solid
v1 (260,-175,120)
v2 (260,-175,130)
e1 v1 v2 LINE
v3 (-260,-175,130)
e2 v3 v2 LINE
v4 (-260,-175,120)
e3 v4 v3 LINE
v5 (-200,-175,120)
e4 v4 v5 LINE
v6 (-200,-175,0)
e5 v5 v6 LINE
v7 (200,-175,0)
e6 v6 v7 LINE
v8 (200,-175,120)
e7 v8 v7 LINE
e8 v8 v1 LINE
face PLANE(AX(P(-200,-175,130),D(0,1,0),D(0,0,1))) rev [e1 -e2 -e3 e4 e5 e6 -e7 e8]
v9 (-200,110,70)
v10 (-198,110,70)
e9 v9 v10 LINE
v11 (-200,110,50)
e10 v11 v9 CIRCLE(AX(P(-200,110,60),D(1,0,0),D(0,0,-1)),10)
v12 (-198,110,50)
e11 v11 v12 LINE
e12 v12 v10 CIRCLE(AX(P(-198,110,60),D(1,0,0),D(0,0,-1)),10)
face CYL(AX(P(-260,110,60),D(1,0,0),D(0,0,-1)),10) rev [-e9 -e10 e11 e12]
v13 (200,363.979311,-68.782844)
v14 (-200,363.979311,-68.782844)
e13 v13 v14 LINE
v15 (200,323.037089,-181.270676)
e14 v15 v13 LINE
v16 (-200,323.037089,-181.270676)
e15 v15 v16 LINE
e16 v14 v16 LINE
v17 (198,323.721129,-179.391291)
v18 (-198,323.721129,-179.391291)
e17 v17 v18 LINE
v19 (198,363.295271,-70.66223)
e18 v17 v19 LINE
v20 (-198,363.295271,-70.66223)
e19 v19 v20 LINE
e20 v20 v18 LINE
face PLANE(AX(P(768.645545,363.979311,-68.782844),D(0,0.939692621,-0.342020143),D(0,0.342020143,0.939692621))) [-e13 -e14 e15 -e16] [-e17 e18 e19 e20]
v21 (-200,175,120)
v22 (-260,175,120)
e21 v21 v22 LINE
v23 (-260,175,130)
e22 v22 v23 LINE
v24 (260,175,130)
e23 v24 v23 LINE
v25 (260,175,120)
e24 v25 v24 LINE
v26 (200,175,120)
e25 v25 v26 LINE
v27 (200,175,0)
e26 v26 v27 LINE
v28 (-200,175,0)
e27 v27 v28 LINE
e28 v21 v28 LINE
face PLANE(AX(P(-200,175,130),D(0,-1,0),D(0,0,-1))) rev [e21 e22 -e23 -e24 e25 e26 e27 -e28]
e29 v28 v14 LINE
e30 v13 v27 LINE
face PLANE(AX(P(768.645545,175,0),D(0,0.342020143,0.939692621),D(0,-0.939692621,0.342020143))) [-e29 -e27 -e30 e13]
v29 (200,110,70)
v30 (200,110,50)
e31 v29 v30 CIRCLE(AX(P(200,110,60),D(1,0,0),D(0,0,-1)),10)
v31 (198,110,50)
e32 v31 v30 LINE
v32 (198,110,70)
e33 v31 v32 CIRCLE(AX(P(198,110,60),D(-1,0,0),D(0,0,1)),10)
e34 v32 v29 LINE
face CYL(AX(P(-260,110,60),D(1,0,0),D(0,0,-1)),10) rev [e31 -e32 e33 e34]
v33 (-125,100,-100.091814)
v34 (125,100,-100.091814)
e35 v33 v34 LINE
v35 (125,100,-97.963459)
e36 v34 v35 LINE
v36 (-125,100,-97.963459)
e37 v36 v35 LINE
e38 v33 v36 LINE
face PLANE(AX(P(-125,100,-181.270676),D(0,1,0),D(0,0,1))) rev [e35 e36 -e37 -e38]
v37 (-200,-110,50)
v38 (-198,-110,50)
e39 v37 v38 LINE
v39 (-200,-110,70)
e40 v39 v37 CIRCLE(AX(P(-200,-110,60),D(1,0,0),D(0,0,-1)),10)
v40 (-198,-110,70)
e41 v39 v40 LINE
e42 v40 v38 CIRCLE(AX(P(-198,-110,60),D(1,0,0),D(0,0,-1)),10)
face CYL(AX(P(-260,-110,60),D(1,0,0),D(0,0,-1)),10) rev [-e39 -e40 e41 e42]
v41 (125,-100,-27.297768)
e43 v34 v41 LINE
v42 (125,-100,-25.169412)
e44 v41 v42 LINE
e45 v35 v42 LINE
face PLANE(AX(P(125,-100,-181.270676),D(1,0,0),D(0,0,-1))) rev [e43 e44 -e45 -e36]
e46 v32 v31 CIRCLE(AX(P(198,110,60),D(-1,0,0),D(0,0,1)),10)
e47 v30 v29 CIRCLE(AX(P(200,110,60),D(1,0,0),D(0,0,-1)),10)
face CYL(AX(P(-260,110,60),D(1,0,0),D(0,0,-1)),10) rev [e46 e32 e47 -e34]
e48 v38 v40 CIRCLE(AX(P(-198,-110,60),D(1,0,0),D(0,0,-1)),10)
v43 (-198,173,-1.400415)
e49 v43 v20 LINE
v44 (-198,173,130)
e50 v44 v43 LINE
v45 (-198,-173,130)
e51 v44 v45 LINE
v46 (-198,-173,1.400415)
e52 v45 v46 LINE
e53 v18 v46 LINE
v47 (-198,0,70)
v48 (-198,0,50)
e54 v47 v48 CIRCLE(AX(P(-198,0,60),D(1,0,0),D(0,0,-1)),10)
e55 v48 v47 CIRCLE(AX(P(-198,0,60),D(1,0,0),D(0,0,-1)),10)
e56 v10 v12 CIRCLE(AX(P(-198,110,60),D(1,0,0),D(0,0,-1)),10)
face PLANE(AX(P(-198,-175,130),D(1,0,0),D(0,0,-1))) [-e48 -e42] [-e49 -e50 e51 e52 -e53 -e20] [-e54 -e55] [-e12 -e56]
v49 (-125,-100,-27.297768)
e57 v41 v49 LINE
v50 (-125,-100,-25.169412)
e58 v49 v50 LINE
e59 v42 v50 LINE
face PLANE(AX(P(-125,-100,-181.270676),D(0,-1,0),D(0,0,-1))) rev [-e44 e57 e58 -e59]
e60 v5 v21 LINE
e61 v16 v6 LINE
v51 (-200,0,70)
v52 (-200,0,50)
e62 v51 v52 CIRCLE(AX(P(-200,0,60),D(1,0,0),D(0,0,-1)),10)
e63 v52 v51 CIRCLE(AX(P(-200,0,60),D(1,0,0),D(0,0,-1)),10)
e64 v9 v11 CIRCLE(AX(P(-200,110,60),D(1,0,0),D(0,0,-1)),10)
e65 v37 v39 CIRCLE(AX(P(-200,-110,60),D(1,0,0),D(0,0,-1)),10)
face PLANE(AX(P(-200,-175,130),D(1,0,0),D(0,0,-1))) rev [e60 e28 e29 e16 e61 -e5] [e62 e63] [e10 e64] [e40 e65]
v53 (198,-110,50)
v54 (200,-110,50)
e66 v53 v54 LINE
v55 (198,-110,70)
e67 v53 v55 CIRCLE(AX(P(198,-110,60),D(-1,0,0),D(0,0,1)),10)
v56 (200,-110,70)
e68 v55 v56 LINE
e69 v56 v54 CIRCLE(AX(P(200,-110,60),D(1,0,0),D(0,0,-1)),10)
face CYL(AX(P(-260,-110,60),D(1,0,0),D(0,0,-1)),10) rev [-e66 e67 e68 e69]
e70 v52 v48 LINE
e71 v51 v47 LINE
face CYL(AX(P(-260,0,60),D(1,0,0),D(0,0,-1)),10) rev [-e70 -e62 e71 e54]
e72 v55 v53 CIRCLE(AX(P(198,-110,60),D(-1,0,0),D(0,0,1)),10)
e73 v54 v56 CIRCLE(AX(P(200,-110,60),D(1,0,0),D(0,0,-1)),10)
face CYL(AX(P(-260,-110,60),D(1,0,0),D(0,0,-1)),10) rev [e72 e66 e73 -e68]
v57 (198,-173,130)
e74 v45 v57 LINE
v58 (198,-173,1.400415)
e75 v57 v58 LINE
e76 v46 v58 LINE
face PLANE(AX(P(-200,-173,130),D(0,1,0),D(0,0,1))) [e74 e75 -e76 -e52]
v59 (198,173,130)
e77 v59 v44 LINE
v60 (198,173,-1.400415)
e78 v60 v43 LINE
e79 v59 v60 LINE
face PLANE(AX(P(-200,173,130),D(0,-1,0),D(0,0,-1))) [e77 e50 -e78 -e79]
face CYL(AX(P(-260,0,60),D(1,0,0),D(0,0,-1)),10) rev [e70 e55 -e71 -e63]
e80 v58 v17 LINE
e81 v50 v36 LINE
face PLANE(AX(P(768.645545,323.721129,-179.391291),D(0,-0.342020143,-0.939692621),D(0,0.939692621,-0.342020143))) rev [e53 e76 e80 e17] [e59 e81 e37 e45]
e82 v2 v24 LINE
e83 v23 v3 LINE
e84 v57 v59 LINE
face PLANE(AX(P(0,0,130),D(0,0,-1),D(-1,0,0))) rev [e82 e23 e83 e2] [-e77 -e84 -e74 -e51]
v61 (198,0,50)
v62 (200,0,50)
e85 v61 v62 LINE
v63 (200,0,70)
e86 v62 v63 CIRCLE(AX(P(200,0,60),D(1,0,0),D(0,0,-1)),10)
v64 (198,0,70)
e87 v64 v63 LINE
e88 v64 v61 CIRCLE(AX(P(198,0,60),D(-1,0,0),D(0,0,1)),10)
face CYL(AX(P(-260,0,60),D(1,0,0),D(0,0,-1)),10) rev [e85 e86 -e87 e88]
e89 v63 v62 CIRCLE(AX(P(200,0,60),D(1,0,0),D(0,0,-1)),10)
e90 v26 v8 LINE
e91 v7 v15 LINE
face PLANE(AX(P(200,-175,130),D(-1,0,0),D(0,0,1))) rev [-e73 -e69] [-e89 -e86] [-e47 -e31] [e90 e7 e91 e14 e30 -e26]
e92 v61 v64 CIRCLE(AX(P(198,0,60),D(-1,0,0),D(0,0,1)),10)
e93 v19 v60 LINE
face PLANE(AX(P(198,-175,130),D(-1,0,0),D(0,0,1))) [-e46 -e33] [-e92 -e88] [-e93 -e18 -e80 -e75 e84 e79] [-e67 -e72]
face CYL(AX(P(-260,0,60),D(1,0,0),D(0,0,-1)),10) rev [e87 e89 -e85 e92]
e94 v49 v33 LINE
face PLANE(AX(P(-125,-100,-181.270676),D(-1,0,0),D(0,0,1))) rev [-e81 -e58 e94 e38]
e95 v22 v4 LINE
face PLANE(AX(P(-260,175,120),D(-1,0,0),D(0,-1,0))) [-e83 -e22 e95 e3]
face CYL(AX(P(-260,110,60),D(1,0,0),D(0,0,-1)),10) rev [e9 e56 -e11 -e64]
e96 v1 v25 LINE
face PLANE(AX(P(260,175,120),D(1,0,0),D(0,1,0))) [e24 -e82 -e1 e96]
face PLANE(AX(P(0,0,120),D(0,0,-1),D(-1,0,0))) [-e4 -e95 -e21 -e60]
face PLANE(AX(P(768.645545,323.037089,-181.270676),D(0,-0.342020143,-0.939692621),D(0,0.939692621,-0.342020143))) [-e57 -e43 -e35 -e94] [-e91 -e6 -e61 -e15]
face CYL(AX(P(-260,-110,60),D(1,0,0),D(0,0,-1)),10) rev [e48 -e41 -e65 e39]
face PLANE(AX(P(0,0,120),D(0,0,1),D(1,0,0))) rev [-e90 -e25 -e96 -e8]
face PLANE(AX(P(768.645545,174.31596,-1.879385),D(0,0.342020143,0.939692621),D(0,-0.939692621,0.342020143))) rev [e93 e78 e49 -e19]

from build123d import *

# Parameters (mm, degrees)
SKETCH_1_W          = 400
SKETCH_1_H          = 350
EXTRUDE_1_DEPTH     = 130
EXTRUDE_5_DEPTH     = 400
SHELL_2_T           = -2
SKETCH_3_W          = 60
SKETCH_3_H          = 350
EXTRUDE_2_DEPTH     = 10
SKETCH_8_W          = 250
SKETCH_8_H          = 200
CUT_EXTRUDE_1_DEPTH = 545.949881083
SKETCH_9_R          = 10
CUT_EXTRUDE_2_DEPTH = 614.954393374


with BuildPart() as part:
    # 草图1 → 凸台-拉伸1 (new body)
    with BuildSketch(Plane.XY):
        Rectangle(SKETCH_1_W, SKETCH_1_H)
    extrude(amount=EXTRUDE_1_DEPTH)

    # 草图7 → 凸台-拉伸5 (add)
    with BuildSketch(Plane.ZY.offset(200)):
        Polygon((0, 175), (-68.782844267, 363.979311471), (-181.270675963, 323.037089017), (0, -175), align=None)
    extrude(amount=-EXTRUDE_5_DEPTH)

    # 抽壳2
    shell_2_openings = [part.faces().sort_by_distance(p)[0] for p in [
        (0, 0, 130),
        (0, 343.508200244, -125.026760115),
    ]]
    offset(amount=SHELL_2_T, openings=shell_2_openings, kind=Kind.INTERSECTION)

    # 草图3 → 凸台-拉伸2 (add)
    with BuildSketch(Plane.XY.offset(130)):
        with Locations((-230, 0)):
            Rectangle(SKETCH_3_W, SKETCH_3_H)
        with Locations((230, 0)):
            Rectangle(SKETCH_3_W, SKETCH_3_H)
    extrude(amount=-EXTRUDE_2_DEPTH)

    # 草图8 → 切除-拉伸1 (cut, through all)
    with BuildSketch(Plane.XY.offset(130)):
        Rectangle(SKETCH_8_W, SKETCH_8_H)
    extrude(amount=-CUT_EXTRUDE_1_DEPTH, mode=Mode.SUBTRACT)

    # 草图9 → 切除-拉伸2 (cut, through all)
    with BuildSketch(Plane(origin=(200, 0, 0), x_dir=(0, 0, -1), z_dir=(1, 0, 0))):
        with Locations((-60, 110)):
            Circle(SKETCH_9_R)
        with Locations((-60, -110)):
            Circle(SKETCH_9_R)
        with Locations((-60, 0)):
            Circle(SKETCH_9_R)
    extrude(amount=-CUT_EXTRUDE_2_DEPTH, mode=Mode.SUBTRACT)


solid = part.part
